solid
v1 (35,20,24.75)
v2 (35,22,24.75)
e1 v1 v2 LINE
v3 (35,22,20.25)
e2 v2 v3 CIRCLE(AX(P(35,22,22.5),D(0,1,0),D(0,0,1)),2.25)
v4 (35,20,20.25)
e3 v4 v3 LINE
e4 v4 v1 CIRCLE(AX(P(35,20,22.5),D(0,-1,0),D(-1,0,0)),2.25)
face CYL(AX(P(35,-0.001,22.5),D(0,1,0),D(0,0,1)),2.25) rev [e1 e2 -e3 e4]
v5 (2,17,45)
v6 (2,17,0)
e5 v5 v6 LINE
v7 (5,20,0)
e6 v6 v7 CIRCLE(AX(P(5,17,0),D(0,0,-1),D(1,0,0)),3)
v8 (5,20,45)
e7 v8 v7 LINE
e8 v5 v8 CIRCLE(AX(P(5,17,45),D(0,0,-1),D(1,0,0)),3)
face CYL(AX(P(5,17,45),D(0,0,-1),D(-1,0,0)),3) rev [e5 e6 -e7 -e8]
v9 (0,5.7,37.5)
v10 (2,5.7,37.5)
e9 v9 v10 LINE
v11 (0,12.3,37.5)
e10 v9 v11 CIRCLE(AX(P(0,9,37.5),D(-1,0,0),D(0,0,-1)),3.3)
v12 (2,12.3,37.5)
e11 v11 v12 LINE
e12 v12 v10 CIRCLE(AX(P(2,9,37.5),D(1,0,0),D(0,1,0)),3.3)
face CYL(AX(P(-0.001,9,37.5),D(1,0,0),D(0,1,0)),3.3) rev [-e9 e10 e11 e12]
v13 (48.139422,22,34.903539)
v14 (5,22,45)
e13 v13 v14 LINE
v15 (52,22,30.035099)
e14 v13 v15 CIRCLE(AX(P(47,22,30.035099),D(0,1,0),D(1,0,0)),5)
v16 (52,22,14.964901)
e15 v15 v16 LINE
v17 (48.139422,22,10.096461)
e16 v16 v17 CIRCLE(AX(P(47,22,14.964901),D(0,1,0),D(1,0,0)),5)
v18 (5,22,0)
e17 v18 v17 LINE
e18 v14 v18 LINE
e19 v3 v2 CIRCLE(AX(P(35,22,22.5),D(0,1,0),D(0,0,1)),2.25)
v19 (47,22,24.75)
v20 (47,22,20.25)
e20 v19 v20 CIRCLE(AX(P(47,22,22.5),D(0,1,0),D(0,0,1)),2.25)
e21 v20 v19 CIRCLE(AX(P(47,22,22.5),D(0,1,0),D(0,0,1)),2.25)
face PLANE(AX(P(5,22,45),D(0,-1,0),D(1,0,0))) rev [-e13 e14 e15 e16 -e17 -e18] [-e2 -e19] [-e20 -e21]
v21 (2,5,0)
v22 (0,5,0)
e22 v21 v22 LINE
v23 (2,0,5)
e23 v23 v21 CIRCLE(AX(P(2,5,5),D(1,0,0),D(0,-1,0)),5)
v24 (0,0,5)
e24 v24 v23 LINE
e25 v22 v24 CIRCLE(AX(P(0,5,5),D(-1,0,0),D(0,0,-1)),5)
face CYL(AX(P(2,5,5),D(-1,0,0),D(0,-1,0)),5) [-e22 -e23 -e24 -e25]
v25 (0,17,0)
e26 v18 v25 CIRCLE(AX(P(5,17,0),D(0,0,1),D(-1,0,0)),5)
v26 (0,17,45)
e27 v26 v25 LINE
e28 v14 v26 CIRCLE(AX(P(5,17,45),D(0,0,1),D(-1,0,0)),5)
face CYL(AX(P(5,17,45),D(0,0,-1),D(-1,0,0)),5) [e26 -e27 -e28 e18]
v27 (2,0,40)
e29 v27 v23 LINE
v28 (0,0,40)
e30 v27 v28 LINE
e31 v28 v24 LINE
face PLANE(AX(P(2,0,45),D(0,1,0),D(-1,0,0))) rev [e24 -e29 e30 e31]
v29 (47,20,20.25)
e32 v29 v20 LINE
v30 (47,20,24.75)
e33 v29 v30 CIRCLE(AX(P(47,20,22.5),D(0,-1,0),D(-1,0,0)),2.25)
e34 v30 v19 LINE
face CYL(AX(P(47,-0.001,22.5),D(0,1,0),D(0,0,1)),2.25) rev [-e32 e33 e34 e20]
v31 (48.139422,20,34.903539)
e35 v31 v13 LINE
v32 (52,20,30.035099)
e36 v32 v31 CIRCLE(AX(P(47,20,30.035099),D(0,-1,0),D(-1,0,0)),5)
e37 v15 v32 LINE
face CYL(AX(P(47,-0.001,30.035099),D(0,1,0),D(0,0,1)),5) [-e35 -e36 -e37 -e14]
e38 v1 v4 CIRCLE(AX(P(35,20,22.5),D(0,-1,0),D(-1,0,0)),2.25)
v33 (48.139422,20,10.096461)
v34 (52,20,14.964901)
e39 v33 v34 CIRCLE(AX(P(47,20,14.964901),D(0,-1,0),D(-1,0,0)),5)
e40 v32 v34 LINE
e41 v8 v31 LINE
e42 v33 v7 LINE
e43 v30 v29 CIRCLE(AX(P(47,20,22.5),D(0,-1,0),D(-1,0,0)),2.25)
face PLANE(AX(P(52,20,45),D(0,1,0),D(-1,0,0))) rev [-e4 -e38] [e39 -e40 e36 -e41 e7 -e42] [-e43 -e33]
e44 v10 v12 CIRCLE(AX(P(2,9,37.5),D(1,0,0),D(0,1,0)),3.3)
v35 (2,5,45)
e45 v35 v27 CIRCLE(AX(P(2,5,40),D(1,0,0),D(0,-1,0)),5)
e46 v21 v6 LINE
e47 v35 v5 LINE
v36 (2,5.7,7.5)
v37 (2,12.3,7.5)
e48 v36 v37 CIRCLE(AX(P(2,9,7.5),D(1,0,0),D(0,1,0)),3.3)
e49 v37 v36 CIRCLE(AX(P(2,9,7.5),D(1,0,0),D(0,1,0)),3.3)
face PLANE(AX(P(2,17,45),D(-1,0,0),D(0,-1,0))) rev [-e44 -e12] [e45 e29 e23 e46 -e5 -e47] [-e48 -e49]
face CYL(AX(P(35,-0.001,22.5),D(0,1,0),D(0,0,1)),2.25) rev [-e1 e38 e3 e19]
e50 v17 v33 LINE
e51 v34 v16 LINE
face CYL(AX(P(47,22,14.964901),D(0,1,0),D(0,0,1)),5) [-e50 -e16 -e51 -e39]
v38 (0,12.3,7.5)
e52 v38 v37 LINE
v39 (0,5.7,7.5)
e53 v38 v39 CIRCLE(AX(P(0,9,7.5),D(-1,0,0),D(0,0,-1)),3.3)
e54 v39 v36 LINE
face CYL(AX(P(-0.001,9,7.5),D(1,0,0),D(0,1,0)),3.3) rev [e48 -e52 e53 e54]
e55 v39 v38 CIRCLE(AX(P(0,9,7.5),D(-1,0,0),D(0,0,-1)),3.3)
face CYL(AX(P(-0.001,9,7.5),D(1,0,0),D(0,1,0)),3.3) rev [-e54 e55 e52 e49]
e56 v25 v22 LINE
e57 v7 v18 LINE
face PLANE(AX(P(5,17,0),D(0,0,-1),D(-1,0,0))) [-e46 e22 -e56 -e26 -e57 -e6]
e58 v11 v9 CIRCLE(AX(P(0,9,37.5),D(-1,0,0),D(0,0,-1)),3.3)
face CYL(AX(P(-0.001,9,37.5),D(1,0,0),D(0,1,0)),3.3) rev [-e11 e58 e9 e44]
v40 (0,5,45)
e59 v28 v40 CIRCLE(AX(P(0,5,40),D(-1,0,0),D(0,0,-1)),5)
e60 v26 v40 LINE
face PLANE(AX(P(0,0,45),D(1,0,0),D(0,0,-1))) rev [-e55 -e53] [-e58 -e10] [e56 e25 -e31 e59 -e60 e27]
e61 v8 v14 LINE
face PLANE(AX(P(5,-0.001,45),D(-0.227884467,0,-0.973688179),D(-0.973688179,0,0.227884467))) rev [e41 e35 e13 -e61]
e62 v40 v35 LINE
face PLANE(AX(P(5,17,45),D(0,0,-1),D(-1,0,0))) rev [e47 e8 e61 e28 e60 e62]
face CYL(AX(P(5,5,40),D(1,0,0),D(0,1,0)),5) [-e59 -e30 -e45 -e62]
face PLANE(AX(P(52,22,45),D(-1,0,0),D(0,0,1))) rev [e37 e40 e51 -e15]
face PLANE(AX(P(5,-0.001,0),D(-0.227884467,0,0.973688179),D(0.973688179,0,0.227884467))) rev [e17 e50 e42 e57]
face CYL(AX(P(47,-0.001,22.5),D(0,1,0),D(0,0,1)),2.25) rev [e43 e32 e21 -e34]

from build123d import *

# Parameters (mm, degrees)
BOSS_EXTRUDE1_DEPTH = 45
CUT_EXTRUDE1_REACH  = 72.774
SKETCH2_R           = 3.3
CUT_EXTRUDE2_REACH  = 74.201
SKETCH3_R           = 2.25
CUT_EXTRUDE3_REACH  = 74.201
FILLET1_R           = 5


with BuildPart() as part:
    # Sketch1 → Boss-Extrude1 (new body)
    with BuildSketch(Plane.XY):
        with BuildLine():
            Line((0, 0), (0, 17))
            ThreePointArc((0, 17), (1.464466094, 20.535533906), (5, 22))
            Line((5, 22), (52, 22))
            Line((52, 22), (52, 20))
            Line((52, 20), (5, 20))
            ThreePointArc((5, 20), (2.878679656, 19.121320344), (2, 17))
            Line((2, 17), (2, 0))
            Line((2, 0), (0, 0))
        make_face()
    extrude(amount=BOSS_EXTRUDE1_DEPTH)

    # Sketch2 → Cut-Extrude1 (cut, up to next)
    with BuildSketch(Plane(origin=(2, 0, 0), x_dir=(0, 0, -1), z_dir=(1, 0, 0)), mode=Mode.PRIVATE) as cut_extrude1_sk1:
        with Locations(Location((-37.5, 9, 0), (0, 0, 90))):
            Circle(SKETCH2_R)
    cut_extrude1_tool1 = extrude(cut_extrude1_sk1.sketch, amount=-CUT_EXTRUDE1_REACH, mode=Mode.PRIVATE) & part.part
    # Sketch2 → Cut-Extrude1 (cut, up to next)
    with BuildSketch(Plane(origin=(2, 0, 0), x_dir=(0, 0, -1), z_dir=(1, 0, 0)), mode=Mode.PRIVATE) as cut_extrude1_sk2:
        with Locations(Location((-7.5, 9, 0), (0, 0, 90))):
            Circle(SKETCH2_R)
    cut_extrude1_tool2 = extrude(cut_extrude1_sk2.sketch, amount=-CUT_EXTRUDE1_REACH, mode=Mode.PRIVATE) & part.part
    add(cut_extrude1_tool1.solids().sort_by_distance((2, 9, 37.5))[0], mode=Mode.SUBTRACT)
    add(cut_extrude1_tool2.solids().sort_by_distance((2, 9, 7.5))[0], mode=Mode.SUBTRACT)

    # Sketch3 → Cut-Extrude2 (cut, up to next)
    with BuildSketch(Plane(origin=(0, 22, 0), x_dir=(1, 0, 0), z_dir=(0, 1, 0)), mode=Mode.PRIVATE) as cut_extrude2_sk1:
        with Locations(Location((35, -22.5, 0), (0, 0, 270))):
            Circle(SKETCH3_R)
    cut_extrude2_tool1 = extrude(cut_extrude2_sk1.sketch, amount=-CUT_EXTRUDE2_REACH, mode=Mode.PRIVATE) & part.part
    # Sketch3 → Cut-Extrude2 (cut, up to next)
    with BuildSketch(Plane(origin=(0, 22, 0), x_dir=(1, 0, 0), z_dir=(0, 1, 0)), mode=Mode.PRIVATE) as cut_extrude2_sk2:
        with Locations(Location((47, -22.5, 0), (0, 0, 270))):
            Circle(SKETCH3_R)
    cut_extrude2_tool2 = extrude(cut_extrude2_sk2.sketch, amount=-CUT_EXTRUDE2_REACH, mode=Mode.PRIVATE) & part.part
    add(cut_extrude2_tool1.solids().sort_by_distance((35, 22, 22.5))[0], mode=Mode.SUBTRACT)
    add(cut_extrude2_tool2.solids().sort_by_distance((47, 22, 22.5))[0], mode=Mode.SUBTRACT)

    # Sketch4 → Cut-Extrude3 (cut, up to next)
    with BuildSketch(Plane(origin=(0, 22, 0), x_dir=(1, 0, 0), z_dir=(0, 1, 0)), mode=Mode.PRIVATE) as cut_extrude3_sk1:
        Polygon((5, 0), (52, -11), (52, 0), align=None)
    cut_extrude3_tool1 = extrude(cut_extrude3_sk1.sketch, amount=-CUT_EXTRUDE3_REACH, mode=Mode.PRIVATE) & part.part
    # Sketch4 → Cut-Extrude3 (cut, up to next)
    with BuildSketch(Plane(origin=(0, 22, 0), x_dir=(1, 0, 0), z_dir=(0, 1, 0)), mode=Mode.PRIVATE) as cut_extrude3_sk2:
        Polygon((5, -45), (52, -34), (52, -45), align=None)
    cut_extrude3_tool2 = extrude(cut_extrude3_sk2.sketch, amount=-CUT_EXTRUDE3_REACH, mode=Mode.PRIVATE) & part.part
    add(cut_extrude3_tool1.solids().sort_by_distance((36.333333, 22, 3.666667))[0], mode=Mode.SUBTRACT)
    add(cut_extrude3_tool2.solids().sort_by_distance((36.333333, 22, 41.333333))[0], mode=Mode.SUBTRACT)

    # Fillet1
    fillet1_edges = [part.edges().sort_by_distance(p)[0] for p in [
        (1, 0, 0),
        (1, 0, 45),
        (52, 21, 11),
        (52, 21, 34),
    ]]
    fillet(fillet1_edges, radius=FILLET1_R)


solid = part.part
